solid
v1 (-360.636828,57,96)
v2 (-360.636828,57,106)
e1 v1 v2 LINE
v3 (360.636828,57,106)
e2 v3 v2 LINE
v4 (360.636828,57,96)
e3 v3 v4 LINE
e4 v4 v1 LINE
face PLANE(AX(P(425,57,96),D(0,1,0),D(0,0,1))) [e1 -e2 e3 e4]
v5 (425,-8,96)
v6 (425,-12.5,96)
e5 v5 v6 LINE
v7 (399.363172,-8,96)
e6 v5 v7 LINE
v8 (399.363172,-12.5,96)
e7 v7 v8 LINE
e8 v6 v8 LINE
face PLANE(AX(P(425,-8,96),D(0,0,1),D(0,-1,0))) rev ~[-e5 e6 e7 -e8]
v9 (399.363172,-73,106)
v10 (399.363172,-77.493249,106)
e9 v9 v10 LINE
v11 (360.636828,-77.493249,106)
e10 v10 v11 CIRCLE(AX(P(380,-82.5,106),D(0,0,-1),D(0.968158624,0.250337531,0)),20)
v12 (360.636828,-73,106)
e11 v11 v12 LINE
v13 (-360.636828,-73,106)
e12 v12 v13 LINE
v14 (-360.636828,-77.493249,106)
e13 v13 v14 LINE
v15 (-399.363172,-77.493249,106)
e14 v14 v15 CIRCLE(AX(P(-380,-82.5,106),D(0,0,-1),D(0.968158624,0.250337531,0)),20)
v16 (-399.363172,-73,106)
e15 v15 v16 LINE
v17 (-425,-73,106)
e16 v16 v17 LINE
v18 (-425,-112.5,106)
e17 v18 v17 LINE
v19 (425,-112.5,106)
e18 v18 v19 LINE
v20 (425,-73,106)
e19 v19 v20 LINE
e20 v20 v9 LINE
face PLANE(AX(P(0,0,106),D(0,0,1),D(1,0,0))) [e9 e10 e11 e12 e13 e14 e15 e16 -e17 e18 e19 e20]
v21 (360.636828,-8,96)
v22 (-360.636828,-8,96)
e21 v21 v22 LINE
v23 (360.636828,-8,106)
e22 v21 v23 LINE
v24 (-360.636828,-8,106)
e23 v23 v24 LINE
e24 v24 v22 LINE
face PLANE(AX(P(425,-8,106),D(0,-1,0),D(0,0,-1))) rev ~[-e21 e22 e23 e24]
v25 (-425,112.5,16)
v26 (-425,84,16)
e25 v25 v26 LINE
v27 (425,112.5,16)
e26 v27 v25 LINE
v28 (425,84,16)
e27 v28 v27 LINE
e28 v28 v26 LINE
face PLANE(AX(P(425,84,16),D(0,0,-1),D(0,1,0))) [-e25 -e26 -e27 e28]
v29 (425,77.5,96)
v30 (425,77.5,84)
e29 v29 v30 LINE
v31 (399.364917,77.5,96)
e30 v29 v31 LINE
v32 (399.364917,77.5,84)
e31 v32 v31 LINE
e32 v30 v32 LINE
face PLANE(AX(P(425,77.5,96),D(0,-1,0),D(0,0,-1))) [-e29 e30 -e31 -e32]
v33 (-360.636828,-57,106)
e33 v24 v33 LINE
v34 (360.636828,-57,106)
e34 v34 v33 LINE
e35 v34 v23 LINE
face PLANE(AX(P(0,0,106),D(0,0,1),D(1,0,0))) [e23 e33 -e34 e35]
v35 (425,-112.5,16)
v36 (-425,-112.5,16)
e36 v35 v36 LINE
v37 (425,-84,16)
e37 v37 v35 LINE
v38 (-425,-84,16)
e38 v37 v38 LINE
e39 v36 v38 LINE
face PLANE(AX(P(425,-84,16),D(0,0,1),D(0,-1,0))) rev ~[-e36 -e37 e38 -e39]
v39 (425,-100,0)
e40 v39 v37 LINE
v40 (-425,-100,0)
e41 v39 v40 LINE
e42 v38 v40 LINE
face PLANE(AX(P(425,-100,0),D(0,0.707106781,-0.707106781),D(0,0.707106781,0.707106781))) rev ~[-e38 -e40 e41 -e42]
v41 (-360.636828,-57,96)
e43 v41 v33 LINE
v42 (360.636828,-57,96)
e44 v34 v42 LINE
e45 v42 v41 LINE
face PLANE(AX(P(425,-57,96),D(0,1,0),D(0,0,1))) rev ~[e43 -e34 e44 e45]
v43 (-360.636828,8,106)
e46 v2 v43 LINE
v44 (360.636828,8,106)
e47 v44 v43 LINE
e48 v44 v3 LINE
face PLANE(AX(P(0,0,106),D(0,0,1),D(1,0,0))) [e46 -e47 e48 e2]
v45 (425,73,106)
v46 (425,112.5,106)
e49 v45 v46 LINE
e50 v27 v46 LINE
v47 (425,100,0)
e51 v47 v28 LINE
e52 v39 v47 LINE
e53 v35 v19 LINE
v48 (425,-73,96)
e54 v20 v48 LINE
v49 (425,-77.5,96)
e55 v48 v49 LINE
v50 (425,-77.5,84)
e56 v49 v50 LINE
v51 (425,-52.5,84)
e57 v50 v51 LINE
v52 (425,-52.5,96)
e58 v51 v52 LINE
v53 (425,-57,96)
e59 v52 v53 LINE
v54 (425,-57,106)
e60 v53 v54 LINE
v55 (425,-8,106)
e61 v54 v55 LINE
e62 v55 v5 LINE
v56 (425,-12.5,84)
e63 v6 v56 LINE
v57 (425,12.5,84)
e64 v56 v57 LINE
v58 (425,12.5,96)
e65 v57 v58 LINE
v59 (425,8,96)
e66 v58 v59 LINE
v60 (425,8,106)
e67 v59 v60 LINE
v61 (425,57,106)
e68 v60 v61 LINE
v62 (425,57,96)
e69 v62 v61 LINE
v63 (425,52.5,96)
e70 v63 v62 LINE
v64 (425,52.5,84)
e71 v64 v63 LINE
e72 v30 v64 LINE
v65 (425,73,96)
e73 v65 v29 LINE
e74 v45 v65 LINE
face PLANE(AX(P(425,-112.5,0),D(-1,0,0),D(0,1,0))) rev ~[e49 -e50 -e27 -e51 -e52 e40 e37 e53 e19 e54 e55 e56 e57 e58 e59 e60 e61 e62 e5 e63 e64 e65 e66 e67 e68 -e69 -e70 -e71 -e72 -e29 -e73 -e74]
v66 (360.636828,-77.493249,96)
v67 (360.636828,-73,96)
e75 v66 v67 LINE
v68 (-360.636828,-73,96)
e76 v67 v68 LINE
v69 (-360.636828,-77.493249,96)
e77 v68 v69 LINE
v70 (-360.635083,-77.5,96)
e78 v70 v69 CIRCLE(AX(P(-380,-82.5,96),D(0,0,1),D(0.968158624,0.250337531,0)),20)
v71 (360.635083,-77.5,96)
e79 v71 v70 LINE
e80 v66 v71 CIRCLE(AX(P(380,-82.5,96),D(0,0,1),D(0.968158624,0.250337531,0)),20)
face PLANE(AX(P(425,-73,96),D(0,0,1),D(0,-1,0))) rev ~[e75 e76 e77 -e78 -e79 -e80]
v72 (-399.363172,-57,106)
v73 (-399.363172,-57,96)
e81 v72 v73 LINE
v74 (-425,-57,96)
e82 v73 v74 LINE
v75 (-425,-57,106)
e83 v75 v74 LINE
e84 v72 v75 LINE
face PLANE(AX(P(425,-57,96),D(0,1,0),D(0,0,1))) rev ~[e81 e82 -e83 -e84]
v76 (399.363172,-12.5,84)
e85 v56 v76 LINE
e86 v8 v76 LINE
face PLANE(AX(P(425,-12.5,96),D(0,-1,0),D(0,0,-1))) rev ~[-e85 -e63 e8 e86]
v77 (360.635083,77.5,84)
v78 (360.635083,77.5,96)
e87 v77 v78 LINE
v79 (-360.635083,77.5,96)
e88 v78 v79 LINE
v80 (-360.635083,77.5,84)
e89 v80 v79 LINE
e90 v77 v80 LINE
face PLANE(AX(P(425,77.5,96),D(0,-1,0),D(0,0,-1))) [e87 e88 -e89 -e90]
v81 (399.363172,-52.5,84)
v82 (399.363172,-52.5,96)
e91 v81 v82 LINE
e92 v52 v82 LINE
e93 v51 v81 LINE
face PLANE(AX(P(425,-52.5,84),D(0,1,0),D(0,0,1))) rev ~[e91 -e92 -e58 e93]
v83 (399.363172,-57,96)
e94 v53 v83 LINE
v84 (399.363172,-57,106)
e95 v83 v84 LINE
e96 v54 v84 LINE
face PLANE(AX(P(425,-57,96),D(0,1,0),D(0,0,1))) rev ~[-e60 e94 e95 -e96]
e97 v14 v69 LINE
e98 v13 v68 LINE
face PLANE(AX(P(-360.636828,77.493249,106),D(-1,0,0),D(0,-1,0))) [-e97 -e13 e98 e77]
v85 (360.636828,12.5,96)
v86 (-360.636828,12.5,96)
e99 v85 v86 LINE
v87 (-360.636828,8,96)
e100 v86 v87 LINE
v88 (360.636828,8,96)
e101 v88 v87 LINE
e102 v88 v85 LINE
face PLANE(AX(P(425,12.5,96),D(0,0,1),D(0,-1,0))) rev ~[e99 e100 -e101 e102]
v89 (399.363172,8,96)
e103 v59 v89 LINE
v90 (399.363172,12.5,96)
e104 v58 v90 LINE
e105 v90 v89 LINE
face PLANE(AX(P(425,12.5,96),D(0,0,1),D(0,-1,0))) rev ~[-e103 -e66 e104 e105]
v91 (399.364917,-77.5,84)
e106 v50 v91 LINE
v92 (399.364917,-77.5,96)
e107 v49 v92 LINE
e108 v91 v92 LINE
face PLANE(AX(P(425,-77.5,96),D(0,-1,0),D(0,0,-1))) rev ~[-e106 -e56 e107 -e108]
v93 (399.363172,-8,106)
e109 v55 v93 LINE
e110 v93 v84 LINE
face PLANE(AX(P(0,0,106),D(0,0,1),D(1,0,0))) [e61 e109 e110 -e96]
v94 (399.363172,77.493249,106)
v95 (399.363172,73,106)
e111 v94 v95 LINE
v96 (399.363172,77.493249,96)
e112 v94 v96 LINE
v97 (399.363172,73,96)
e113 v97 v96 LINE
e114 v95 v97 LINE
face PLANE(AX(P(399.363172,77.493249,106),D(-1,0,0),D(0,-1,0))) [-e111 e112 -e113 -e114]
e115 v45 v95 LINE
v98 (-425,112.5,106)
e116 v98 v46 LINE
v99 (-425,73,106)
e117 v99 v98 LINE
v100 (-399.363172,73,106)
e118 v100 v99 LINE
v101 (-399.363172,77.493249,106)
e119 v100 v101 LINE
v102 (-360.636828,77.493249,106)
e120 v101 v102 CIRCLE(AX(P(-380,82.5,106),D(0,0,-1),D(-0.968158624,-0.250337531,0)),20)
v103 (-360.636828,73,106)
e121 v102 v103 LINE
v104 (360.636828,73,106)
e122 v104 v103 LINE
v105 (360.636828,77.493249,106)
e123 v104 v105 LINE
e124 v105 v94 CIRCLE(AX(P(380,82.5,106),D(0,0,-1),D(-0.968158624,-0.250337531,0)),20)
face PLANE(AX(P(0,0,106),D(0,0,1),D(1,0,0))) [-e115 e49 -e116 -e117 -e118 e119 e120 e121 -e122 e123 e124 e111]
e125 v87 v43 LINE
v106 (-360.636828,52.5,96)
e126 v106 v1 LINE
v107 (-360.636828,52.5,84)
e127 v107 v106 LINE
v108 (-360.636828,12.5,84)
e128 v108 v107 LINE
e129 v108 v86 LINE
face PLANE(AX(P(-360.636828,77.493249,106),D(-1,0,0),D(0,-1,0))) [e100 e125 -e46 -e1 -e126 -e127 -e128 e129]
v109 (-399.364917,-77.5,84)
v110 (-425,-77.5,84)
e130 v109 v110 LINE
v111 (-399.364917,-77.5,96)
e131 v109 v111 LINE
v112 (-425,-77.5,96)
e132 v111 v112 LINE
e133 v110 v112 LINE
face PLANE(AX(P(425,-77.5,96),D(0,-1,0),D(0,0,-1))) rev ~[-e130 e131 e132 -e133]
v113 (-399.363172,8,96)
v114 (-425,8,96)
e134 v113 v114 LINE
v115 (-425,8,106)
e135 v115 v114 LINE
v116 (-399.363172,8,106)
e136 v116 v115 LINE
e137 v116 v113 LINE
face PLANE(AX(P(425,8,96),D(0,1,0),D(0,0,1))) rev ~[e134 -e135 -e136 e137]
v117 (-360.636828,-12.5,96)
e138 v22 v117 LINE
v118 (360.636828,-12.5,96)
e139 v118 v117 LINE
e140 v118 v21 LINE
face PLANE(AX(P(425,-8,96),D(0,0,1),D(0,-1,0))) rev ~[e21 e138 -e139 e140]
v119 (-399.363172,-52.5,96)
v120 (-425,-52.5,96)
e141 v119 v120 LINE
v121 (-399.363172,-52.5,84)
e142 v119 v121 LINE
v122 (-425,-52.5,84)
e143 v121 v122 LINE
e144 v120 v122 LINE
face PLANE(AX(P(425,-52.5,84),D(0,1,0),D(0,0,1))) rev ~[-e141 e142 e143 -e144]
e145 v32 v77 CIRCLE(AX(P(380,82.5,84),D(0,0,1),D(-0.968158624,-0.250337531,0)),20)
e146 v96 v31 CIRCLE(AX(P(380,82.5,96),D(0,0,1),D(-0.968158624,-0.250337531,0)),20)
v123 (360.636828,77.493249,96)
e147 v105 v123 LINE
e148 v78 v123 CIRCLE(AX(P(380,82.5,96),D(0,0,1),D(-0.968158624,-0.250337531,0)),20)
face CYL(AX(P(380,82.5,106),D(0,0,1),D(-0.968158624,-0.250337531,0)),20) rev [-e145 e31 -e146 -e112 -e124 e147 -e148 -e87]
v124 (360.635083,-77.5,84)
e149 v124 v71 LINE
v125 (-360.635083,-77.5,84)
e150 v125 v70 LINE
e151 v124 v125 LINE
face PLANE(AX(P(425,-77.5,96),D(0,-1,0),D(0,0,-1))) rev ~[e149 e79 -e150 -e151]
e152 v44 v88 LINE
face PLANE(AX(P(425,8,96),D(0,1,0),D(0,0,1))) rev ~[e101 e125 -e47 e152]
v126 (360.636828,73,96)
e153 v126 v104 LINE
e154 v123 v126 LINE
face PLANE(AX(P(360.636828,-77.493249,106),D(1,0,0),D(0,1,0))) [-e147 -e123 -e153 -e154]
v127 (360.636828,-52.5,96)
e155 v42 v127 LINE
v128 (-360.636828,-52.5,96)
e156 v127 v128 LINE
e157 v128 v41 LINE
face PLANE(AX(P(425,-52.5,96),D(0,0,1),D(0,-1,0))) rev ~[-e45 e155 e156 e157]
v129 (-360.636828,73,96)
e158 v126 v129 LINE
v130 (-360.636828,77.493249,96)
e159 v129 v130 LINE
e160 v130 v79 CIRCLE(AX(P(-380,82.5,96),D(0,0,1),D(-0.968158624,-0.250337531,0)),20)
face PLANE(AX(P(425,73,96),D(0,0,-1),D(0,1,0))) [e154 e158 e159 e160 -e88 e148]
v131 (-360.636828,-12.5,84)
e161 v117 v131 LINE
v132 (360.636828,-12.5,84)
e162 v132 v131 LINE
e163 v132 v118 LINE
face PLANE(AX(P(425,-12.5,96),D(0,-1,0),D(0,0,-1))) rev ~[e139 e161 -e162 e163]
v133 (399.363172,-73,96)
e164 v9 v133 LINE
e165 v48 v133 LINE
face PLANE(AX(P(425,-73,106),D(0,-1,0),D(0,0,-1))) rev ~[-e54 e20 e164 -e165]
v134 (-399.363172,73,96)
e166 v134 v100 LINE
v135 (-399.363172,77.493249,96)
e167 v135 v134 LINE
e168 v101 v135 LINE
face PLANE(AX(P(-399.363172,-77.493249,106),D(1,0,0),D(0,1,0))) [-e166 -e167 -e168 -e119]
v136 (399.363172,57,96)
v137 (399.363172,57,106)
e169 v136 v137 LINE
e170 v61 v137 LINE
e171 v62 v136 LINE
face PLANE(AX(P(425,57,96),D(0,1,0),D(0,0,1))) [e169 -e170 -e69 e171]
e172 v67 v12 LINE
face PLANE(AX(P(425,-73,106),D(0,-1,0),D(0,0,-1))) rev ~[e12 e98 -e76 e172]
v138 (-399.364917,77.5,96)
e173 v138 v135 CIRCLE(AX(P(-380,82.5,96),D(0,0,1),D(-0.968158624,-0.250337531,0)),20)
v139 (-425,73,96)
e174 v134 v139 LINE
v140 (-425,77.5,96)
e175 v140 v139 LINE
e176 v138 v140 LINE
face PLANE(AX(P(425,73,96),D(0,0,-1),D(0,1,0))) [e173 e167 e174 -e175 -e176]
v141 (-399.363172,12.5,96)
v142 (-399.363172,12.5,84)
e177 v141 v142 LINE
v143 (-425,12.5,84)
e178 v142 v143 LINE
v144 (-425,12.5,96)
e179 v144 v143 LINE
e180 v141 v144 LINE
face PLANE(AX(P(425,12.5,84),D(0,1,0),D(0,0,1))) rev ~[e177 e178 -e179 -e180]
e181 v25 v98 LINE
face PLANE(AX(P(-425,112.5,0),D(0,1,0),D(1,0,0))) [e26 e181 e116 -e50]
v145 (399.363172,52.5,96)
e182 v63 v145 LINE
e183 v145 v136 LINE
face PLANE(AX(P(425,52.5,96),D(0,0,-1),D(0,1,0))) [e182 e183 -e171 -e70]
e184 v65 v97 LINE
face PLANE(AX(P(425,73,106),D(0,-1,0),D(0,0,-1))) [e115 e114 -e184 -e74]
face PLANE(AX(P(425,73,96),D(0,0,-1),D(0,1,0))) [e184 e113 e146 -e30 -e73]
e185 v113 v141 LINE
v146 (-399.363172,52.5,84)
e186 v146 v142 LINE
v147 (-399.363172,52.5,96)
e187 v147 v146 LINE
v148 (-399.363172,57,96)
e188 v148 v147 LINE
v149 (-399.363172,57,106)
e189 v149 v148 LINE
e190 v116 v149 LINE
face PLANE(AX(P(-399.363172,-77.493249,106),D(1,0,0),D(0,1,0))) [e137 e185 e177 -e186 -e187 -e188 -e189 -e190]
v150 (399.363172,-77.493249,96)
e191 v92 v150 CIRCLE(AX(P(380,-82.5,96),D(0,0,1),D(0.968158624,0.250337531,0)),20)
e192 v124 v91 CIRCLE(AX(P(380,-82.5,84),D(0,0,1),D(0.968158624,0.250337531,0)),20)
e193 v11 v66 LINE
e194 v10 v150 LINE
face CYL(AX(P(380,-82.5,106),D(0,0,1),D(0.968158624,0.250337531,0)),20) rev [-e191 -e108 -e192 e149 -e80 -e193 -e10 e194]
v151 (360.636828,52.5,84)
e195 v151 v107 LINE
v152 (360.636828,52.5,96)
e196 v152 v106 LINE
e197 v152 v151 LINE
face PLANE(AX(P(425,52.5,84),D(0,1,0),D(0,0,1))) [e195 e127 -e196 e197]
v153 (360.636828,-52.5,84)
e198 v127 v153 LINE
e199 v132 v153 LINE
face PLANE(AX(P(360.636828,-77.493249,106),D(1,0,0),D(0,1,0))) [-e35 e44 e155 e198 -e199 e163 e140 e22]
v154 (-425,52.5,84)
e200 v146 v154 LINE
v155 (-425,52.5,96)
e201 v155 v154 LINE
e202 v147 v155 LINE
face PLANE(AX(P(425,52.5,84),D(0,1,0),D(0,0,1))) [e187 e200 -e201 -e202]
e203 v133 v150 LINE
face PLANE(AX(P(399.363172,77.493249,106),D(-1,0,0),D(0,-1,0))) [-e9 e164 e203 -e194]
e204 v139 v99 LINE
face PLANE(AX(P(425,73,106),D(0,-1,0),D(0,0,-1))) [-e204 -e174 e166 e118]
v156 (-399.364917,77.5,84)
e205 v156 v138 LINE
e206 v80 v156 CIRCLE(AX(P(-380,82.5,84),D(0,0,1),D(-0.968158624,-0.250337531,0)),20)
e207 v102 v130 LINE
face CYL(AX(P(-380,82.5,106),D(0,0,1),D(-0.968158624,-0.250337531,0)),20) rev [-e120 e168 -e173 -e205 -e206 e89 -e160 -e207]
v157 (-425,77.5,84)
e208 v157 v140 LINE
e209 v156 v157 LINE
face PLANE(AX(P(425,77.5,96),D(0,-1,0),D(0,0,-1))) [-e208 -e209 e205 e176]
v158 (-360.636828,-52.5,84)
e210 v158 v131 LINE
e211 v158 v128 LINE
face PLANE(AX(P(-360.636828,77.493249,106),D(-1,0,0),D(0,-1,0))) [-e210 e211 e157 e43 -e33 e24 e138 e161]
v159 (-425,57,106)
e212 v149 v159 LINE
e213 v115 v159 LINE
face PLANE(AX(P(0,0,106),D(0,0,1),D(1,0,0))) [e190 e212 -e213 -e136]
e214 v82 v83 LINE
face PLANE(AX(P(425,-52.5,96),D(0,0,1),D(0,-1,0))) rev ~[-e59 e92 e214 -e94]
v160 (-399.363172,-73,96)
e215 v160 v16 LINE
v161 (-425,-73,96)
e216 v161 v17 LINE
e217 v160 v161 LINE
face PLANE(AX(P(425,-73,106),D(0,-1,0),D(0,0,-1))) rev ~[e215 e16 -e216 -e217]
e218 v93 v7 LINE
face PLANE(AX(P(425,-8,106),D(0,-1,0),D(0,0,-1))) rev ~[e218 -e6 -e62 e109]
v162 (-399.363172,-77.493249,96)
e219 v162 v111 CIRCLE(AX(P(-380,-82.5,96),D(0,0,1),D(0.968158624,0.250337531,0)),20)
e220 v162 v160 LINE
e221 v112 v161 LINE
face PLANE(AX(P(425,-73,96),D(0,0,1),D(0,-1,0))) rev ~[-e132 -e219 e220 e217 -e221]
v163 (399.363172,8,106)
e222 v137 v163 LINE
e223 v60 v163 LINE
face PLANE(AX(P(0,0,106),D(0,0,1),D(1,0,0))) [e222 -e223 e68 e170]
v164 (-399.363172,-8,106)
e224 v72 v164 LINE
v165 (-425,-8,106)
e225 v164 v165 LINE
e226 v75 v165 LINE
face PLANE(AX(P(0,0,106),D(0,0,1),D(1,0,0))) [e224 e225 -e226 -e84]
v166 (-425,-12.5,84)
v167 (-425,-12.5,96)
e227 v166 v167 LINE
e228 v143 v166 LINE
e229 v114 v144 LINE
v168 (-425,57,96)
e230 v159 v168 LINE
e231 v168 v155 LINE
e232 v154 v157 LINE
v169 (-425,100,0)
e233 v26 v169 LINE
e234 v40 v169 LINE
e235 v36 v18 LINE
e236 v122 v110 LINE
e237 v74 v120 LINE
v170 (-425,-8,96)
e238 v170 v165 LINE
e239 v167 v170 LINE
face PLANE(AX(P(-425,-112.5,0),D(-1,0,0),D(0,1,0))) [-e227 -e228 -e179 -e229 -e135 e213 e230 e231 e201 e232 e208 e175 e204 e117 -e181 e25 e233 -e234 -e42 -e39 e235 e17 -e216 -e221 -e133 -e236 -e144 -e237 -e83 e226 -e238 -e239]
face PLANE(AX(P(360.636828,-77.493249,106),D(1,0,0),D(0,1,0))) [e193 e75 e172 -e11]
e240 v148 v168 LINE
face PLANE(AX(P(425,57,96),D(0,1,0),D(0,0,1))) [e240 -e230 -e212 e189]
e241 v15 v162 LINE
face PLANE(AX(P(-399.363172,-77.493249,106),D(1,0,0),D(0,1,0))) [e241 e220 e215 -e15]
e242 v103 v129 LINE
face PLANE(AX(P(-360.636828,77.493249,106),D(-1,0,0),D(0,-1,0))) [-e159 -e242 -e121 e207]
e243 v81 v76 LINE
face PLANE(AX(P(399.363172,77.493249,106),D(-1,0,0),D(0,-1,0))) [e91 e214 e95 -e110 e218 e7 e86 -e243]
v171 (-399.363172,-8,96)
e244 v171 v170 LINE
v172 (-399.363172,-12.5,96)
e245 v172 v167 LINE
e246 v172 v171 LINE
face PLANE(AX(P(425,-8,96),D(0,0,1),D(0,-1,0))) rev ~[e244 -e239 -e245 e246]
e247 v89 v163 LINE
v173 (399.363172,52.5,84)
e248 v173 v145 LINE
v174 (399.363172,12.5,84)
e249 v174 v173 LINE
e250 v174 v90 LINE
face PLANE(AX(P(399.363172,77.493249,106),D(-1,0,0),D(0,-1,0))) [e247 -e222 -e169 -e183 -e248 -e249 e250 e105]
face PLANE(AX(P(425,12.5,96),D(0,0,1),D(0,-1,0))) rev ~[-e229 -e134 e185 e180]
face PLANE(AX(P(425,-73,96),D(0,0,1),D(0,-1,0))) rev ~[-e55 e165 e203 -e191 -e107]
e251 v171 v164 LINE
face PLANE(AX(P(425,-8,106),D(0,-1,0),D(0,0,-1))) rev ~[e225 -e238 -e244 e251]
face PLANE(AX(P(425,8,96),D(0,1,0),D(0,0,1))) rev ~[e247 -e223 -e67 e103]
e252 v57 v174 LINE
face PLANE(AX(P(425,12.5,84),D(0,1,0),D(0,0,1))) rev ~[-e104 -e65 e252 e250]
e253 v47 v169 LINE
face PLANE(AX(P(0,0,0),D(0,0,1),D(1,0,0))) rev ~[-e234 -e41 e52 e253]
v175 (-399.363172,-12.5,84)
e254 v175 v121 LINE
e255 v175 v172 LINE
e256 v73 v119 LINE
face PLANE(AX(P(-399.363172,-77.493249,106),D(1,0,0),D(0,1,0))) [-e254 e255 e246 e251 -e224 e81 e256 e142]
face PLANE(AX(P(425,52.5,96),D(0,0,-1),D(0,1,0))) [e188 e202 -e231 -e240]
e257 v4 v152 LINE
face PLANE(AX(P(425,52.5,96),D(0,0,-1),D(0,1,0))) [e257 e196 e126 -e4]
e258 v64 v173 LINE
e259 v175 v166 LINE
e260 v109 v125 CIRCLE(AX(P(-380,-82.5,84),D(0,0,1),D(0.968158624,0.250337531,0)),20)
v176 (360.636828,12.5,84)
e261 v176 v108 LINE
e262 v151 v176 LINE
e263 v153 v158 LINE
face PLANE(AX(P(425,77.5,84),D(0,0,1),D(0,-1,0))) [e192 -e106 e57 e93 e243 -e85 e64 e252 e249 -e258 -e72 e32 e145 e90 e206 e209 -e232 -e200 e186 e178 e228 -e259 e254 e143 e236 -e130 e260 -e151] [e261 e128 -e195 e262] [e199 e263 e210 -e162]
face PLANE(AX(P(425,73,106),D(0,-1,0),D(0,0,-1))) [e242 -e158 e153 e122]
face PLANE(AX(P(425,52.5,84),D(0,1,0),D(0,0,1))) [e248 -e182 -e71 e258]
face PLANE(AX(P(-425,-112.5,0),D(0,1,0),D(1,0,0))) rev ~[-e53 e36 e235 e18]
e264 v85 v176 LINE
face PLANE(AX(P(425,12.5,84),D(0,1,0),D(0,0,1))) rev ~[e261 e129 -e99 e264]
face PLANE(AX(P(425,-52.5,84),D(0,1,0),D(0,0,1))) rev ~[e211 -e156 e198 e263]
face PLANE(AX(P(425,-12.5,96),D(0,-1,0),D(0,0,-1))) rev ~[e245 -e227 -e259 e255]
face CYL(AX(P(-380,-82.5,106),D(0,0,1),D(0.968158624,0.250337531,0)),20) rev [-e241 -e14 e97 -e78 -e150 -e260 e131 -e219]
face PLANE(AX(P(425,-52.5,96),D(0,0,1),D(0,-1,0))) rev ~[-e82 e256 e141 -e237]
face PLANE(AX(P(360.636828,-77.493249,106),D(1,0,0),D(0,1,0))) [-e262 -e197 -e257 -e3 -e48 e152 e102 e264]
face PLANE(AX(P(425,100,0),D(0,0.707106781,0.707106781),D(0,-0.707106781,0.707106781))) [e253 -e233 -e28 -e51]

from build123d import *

# Parameters (mm, degrees)
BASE_BLOCK_PROFILE_W         = 850
BASE_BLOCK_PROFILE_H         = 225
BASE_BLOCK_850X225X106_DEPTH = 106
V_GROOVE_45DEG_DEPTH         = 864.939957404
T_SLOTS_2X_DEPTH             = 864.939957404
T_SLOT_END_POCKETS_REACH     = 454.236


with BuildPart() as part:
    # Base Block Profile → Base Block 850x225x106 (new body)
    with BuildSketch(Plane.XY):
        Rectangle(BASE_BLOCK_PROFILE_W, BASE_BLOCK_PROFILE_H)
    extrude(amount=BASE_BLOCK_850X225X106_DEPTH)

    # V-Groove Profile → V-Groove 45deg (cut, through all)
    with BuildSketch(Plane(origin=(425, 0, 0), x_dir=(0, 0, -1), z_dir=(1, 0, 0))):
        Polygon((-16, -112.5), (0, -112.5), (0, -100), (-16, -84), align=None)
        Polygon((-16, 84), (-16, 112.5), (0, 112.5), (0, 100), align=None)
    extrude(amount=-V_GROOVE_45DEG_DEPTH, mode=Mode.SUBTRACT)

    # T-Slots Profile → T-Slots 2x (cut, through all)
    with BuildSketch(Plane(origin=(425, 0, 0), x_dir=(0, 0, -1), z_dir=(1, 0, 0))):
        Polygon((-96, -12.5), (-84, -12.5), (-84, 12.5), (-96, 12.5), (-96, 8), (-106, 8), (-106, -8), (-96, -8), align=None)
        Polygon((-84, 77.5), (-84, 52.5), (-96, 52.5), (-96, 57), (-106, 57), (-106, 73), (-96, 73), (-96, 77.5), align=None)
        Polygon((-96, -77.5), (-84, -77.5), (-84, -52.5), (-96, -52.5), (-96, -57), (-106, -57), (-106, -73), (-96, -73), align=None)
    extrude(amount=-T_SLOTS_2X_DEPTH, mode=Mode.SUBTRACT)

    # T-Slot End Pockets: up to this face of the body (flat: up to its plane)
    t_slot_end_pockets_end = Plane(part.part.faces().sort_by_distance((0, 0, 84))[0])
    # T-Slot End Pockets Profile → T-Slot End Pockets (cut, up to the picked face)
    with BuildSketch(Plane.XY.offset(106), mode=Mode.PRIVATE) as t_slot_end_pockets_sk1:
        with BuildLine():
            Line((-399.363172475, -77.493249387), (-399.363172475, 77.493249387))
            ThreePointArc((-399.363172475, 77.493249387), (-380, 102.5), (-360.636827525, 77.493249387))
            Line((-360.636827525, 77.493249387), (-360.636827525, -77.493249387))
            ThreePointArc((-360.636827525, -77.493249387), (-380, -102.5), (-399.363172475, -77.493249387))
        make_face()
    t_slot_end_pockets_tool1 = split(extrude(t_slot_end_pockets_sk1.sketch, amount=-T_SLOT_END_POCKETS_REACH, mode=Mode.PRIVATE), bisect_by=t_slot_end_pockets_end, keep=Keep.BOTH, mode=Mode.PRIVATE)
    # T-Slot End Pockets Profile → T-Slot End Pockets (cut, up to the picked face)
    with BuildSketch(Plane.XY.offset(106), mode=Mode.PRIVATE) as t_slot_end_pockets_sk2:
        with BuildLine():
            Line((360.636827525, -77.493249387), (360.636827525, 77.493249387))
            ThreePointArc((360.636827525, 77.493249387), (380, 102.5), (399.363172475, 77.493249387))
            Line((399.363172475, 77.493249387), (399.363172475, -77.493249387))
            ThreePointArc((399.363172475, -77.493249387), (380, -102.5), (360.636827525, -77.493249387))
        make_face()
    t_slot_end_pockets_tool2 = split(extrude(t_slot_end_pockets_sk2.sketch, amount=-T_SLOT_END_POCKETS_REACH, mode=Mode.PRIVATE), bisect_by=t_slot_end_pockets_end, keep=Keep.BOTH, mode=Mode.PRIVATE)
    add(t_slot_end_pockets_tool1.solids().sort_by(Axis((-380, 0, 106), (0, 0, -1)))[0], mode=Mode.SUBTRACT)
    add(t_slot_end_pockets_tool2.solids().sort_by(Axis((380, 0, 106), (0, 0, -1)))[0], mode=Mode.SUBTRACT)


solid = part.part
